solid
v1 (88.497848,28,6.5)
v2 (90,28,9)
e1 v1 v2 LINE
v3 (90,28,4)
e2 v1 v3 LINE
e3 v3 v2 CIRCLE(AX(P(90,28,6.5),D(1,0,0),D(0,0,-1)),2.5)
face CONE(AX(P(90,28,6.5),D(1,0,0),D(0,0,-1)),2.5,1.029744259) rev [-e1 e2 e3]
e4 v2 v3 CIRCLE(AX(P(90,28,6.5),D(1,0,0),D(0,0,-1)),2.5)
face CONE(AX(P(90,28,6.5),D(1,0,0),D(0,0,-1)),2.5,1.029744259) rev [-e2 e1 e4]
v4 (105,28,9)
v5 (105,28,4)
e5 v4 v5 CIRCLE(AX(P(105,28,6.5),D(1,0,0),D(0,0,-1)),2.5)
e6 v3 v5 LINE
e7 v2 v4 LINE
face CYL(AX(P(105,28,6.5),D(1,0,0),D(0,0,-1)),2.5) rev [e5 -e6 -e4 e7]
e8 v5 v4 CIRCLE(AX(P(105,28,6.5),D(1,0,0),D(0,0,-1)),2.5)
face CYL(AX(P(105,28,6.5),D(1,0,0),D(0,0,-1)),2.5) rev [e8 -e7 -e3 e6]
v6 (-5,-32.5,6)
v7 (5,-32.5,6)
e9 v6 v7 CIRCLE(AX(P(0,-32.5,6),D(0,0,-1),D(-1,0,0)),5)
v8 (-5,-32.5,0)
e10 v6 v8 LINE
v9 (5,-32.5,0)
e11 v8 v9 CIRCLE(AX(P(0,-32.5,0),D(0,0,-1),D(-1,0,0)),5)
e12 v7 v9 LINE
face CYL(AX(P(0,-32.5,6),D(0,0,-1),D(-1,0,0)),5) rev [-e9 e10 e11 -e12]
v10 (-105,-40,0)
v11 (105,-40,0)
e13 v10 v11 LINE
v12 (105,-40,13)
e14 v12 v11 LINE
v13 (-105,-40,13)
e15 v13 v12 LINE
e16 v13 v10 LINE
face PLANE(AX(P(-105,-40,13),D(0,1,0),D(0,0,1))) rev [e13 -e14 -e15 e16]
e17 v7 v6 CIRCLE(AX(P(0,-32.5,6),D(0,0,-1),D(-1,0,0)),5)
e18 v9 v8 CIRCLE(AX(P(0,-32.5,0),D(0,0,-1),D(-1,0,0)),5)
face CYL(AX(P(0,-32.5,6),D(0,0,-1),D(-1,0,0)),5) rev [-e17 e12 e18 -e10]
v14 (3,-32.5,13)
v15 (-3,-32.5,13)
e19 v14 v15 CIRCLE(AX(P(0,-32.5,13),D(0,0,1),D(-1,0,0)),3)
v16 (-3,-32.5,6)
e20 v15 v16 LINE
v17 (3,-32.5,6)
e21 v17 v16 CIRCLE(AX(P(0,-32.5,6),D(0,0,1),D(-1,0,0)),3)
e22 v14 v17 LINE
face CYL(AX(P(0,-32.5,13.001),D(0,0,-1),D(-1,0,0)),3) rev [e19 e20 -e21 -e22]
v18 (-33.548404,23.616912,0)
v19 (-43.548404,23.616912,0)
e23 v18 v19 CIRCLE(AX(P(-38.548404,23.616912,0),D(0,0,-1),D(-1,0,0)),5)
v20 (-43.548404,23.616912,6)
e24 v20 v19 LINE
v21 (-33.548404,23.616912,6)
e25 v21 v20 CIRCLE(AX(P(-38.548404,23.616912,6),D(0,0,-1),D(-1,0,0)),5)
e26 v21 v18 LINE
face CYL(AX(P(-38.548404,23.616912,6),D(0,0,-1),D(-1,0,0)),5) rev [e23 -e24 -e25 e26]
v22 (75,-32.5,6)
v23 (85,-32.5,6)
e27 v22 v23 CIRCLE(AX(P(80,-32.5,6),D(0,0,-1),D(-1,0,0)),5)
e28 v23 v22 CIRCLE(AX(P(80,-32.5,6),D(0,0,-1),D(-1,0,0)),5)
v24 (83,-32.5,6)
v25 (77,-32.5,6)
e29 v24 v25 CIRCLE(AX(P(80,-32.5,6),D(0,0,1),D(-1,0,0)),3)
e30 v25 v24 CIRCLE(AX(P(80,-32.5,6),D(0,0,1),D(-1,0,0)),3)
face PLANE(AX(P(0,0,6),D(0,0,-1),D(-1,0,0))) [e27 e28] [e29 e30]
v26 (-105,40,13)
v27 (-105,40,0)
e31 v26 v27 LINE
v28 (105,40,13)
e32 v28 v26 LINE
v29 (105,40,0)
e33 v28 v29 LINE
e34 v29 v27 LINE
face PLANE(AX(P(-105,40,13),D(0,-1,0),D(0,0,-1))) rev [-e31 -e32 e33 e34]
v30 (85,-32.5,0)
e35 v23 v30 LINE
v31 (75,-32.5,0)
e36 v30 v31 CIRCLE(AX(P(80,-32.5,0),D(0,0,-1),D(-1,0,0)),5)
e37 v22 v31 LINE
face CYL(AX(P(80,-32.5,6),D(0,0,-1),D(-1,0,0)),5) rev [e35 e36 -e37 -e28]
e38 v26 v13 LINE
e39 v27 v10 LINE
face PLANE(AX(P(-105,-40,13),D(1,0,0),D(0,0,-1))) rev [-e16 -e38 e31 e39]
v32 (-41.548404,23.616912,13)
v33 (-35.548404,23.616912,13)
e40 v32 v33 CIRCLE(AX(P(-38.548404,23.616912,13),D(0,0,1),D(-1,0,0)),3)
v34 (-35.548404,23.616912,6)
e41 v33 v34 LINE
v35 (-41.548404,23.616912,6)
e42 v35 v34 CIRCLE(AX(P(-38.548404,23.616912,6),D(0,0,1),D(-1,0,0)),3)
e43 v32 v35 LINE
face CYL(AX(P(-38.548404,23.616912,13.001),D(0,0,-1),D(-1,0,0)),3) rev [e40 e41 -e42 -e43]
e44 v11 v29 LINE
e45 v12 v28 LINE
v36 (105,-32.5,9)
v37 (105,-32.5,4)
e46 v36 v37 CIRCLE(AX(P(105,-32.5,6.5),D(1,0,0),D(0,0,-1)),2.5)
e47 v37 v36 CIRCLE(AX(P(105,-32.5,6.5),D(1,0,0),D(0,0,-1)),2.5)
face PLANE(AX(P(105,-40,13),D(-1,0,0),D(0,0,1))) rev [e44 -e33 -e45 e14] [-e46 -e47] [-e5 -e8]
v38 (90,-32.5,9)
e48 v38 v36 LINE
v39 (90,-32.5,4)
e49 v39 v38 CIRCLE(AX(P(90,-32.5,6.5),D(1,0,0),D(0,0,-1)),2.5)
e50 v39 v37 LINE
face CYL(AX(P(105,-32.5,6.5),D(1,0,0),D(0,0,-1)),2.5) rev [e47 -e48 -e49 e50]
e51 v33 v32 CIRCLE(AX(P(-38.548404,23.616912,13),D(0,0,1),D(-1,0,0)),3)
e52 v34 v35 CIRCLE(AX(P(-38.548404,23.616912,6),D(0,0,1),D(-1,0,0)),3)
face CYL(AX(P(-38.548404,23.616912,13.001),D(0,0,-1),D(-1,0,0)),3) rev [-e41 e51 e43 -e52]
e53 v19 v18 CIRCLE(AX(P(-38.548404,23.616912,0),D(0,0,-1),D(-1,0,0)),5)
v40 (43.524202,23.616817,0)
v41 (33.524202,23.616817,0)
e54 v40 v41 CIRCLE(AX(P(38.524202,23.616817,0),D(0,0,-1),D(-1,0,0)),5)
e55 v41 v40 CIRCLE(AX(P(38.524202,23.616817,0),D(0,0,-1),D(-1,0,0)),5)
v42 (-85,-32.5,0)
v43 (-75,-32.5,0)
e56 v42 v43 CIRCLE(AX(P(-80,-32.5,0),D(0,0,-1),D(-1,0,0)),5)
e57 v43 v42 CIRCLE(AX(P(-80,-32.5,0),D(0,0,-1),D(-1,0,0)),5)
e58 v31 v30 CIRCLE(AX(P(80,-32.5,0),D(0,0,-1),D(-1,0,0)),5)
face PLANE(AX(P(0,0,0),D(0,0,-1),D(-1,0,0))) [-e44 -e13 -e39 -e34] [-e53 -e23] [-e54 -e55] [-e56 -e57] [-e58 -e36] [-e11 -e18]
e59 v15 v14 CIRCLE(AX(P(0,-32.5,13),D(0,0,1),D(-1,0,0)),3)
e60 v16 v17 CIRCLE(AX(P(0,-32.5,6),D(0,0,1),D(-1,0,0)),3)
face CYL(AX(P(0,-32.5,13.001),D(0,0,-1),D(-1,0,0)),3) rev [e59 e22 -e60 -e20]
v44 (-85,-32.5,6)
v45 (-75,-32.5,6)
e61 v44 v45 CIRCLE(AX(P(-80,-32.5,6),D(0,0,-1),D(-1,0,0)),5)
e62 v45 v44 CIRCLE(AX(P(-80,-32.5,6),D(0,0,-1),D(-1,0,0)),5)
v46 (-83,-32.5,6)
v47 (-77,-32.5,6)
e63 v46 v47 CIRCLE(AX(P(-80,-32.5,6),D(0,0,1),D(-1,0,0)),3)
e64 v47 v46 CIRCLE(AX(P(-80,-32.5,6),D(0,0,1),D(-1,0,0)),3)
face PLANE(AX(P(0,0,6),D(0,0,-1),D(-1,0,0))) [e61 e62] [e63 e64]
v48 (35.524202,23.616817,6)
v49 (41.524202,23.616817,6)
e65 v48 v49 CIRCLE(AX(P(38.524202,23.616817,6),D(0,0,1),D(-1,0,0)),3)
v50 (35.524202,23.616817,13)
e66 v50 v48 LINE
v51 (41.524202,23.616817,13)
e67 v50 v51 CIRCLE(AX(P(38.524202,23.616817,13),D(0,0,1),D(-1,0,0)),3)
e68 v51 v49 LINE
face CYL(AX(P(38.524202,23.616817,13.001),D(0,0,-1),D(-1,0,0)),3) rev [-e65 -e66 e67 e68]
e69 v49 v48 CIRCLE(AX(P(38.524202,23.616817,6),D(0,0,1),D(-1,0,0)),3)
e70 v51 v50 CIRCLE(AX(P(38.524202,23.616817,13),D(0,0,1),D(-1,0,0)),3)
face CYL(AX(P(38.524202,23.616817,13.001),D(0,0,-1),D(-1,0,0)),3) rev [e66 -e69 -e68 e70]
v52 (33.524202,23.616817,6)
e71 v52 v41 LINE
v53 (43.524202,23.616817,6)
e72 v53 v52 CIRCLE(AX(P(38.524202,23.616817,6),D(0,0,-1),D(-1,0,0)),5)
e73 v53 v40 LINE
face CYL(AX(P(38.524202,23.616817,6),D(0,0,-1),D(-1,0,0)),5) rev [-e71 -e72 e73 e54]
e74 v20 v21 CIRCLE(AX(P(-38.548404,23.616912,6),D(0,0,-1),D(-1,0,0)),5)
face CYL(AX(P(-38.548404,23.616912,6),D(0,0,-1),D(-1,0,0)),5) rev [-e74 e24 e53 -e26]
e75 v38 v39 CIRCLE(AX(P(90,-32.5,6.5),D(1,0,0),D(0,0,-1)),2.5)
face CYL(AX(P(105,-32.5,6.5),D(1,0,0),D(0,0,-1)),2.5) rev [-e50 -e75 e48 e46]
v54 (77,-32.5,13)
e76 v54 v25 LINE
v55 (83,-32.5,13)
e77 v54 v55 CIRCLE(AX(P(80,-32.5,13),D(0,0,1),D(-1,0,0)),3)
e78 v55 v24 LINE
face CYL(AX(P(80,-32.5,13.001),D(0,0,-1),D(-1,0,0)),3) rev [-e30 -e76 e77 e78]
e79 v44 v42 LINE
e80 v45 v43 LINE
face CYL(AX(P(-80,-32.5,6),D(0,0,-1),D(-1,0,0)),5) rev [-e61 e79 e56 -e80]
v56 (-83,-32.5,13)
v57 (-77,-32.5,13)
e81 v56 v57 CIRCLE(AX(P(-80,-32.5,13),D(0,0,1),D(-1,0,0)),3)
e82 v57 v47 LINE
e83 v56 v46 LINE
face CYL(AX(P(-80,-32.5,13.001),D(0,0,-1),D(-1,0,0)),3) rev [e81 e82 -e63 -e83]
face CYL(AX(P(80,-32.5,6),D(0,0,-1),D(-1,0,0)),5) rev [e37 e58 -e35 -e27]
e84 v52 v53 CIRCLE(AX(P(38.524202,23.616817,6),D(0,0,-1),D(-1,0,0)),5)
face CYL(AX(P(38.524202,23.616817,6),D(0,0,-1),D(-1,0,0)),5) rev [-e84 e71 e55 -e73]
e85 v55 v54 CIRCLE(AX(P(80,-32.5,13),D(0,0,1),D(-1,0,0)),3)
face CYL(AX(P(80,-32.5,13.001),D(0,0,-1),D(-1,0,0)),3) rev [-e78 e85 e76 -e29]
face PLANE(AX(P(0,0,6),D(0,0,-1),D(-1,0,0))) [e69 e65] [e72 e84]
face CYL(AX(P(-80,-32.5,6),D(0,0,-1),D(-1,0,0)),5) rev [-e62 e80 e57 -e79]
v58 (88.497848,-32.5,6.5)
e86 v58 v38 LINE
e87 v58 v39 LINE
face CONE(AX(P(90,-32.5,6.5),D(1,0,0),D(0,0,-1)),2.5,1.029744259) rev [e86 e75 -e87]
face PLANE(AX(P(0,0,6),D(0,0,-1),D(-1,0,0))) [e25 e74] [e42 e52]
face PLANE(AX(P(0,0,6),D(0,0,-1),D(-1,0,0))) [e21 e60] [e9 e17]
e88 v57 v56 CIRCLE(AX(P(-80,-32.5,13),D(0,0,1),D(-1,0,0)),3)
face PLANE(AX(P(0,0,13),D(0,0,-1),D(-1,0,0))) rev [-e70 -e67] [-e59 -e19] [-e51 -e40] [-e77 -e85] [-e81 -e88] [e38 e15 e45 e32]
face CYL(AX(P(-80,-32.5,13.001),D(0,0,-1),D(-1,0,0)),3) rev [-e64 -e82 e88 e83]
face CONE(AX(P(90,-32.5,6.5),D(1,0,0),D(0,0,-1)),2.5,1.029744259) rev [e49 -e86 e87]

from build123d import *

# Parameters (mm, degrees)
SKETCH1_W                 = 210
SKETCH1_H                 = 80
BOSS_EXTRUDE1_DEPTH       = 13
SKETCH2_R                 = 5
SKETCH2_R_2               = 3
CUT_EXTRUDE1_DEPTH        = 6
CUT_EXTRUDE2_REACH        = 115.111
SKETCH2_5_R               = 3
M6X1_0_TAPPED_HOLE1_D     = 5
M6X1_0_TAPPED_HOLE1_DEPTH = 15
M6X1_0_TAPPED_HOLE1_TIP   = 1.502151548
SKETCH8_R                 = 5
SKETCH8_R_2               = 3
CUT_EXTRUDE3_DEPTH        = 6
CUT_EXTRUDE4_REACH        = 115.111
SKETCH8_4_R               = 3
M6X1_0_TAPPED_HOLE2_D     = 5
M6X1_0_TAPPED_HOLE2_DEPTH = 15
M6X1_0_TAPPED_HOLE2_TIP   = 1.502151548


with BuildPart() as part:
    # Sketch1 → Boss-Extrude1 (new body)
    with BuildSketch(Plane.XY):
        Rectangle(SKETCH1_W, SKETCH1_H)
    extrude(amount=BOSS_EXTRUDE1_DEPTH)

    # Sketch2 → Cut-Extrude1 (cut)
    # profile 1 of 2: a face of its own
    with BuildSketch(Plane(origin=(0, 0, 0), x_dir=(-1, 0, 0), z_dir=(0, 0, -1))):
        with Locations((-38.524202037, 23.616817232)):
            Circle(SKETCH2_R)
        with Locations((-38.524202037, 23.616817232)):
            Circle(SKETCH2_R_2, mode=Mode.SUBTRACT)
    # profile 2 of 2: a face of its own
    with BuildSketch(Plane(origin=(0, 0, 0), x_dir=(-1, 0, 0), z_dir=(0, 0, -1))):
        with Locations((38.548404074, 23.616912244)):
            Circle(SKETCH2_R)
        with Locations((38.548404074, 23.616912244)):
            Circle(SKETCH2_R_2, mode=Mode.SUBTRACT)
    extrude(amount=-CUT_EXTRUDE1_DEPTH, mode=Mode.SUBTRACT)

    # Sketch2<5> → Cut-Extrude2 (cut, up to next)
    with BuildSketch(Plane(origin=(0, 0, 0), x_dir=(-1, 0, 0), z_dir=(0, 0, -1)), mode=Mode.PRIVATE) as cut_extrude2_sk1:
        with Locations((-38.524202037, 23.616817232)):
            Circle(SKETCH2_5_R)
    cut_extrude2_tool1 = extrude(cut_extrude2_sk1.sketch, amount=-CUT_EXTRUDE2_REACH, mode=Mode.PRIVATE) & part.part
    # Sketch2<5> → Cut-Extrude2 (cut, up to next)
    with BuildSketch(Plane(origin=(0, 0, 0), x_dir=(-1, 0, 0), z_dir=(0, 0, -1)), mode=Mode.PRIVATE) as cut_extrude2_sk2:
        with Locations((38.548404074, 23.616912244)):
            Circle(SKETCH2_5_R)
    cut_extrude2_tool2 = extrude(cut_extrude2_sk2.sketch, amount=-CUT_EXTRUDE2_REACH, mode=Mode.PRIVATE) & part.part
    add(cut_extrude2_tool1.solids().sort_by_distance((38.524202, 23.616817, 0))[0], mode=Mode.SUBTRACT)
    add(cut_extrude2_tool2.solids().sort_by_distance((-38.548404, 23.616912, 0))[0], mode=Mode.SUBTRACT)

    # M6x1.0 Tapped Hole1
    with Locations(Plane(origin=(105, -32.5, 6.5), x_dir=(0, 0, 1), z_dir=(1, 0, 0))):
        with Locations((0, 0)):
            Hole(M6X1_0_TAPPED_HOLE1_D / 2, depth=M6X1_0_TAPPED_HOLE1_DEPTH)
            with Locations((0, 0, -(M6X1_0_TAPPED_HOLE1_DEPTH + M6X1_0_TAPPED_HOLE1_TIP / 2))):  # 118° drill point
                Cone(0, M6X1_0_TAPPED_HOLE1_D / 2, M6X1_0_TAPPED_HOLE1_TIP, mode=Mode.SUBTRACT)

    # Sketch8 → Cut-Extrude3 (cut)
    # profile 1 of 3: a face of its own
    with BuildSketch(Plane(origin=(0, 0, 0), x_dir=(-1, 0, 0), z_dir=(0, 0, -1))):
        with Locations((-80, -32.5)):
            Circle(SKETCH8_R)
        with Locations((-80, -32.5)):
            Circle(SKETCH8_R_2, mode=Mode.SUBTRACT)
    # profile 2 of 3: a face of its own
    with BuildSketch(Plane(origin=(0, 0, 0), x_dir=(-1, 0, 0), z_dir=(0, 0, -1))):
        with Locations((80, -32.5)):
            Circle(SKETCH8_R)
        with Locations((80, -32.5)):
            Circle(SKETCH8_R_2, mode=Mode.SUBTRACT)
    # profile 3 of 3: a face of its own
    with BuildSketch(Plane(origin=(0, 0, 0), x_dir=(-1, 0, 0), z_dir=(0, 0, -1))):
        with Locations((0, -32.5)):
            Circle(SKETCH8_R)
        with Locations((0, -32.5)):
            Circle(SKETCH8_R_2, mode=Mode.SUBTRACT)
    extrude(amount=-CUT_EXTRUDE3_DEPTH, mode=Mode.SUBTRACT)

    # Sketch8<4> → Cut-Extrude4 (cut, up to next)
    with BuildSketch(Plane(origin=(0, 0, 0), x_dir=(-1, 0, 0), z_dir=(0, 0, -1)), mode=Mode.PRIVATE) as cut_extrude4_sk1:
        with Locations((-80, -32.5)):
            Circle(SKETCH8_4_R)
    cut_extrude4_tool1 = extrude(cut_extrude4_sk1.sketch, amount=-CUT_EXTRUDE4_REACH, mode=Mode.PRIVATE) & part.part
    # Sketch8<4> → Cut-Extrude4 (cut, up to next)
    with BuildSketch(Plane(origin=(0, 0, 0), x_dir=(-1, 0, 0), z_dir=(0, 0, -1)), mode=Mode.PRIVATE) as cut_extrude4_sk2:
        with Locations((0, -32.5)):
            Circle(SKETCH8_4_R)
    cut_extrude4_tool2 = extrude(cut_extrude4_sk2.sketch, amount=-CUT_EXTRUDE4_REACH, mode=Mode.PRIVATE) & part.part
    # Sketch8<4> → Cut-Extrude4 (cut, up to next)
    with BuildSketch(Plane(origin=(0, 0, 0), x_dir=(-1, 0, 0), z_dir=(0, 0, -1)), mode=Mode.PRIVATE) as cut_extrude4_sk3:
        with Locations((80, -32.5)):
            Circle(SKETCH8_4_R)
    cut_extrude4_tool3 = extrude(cut_extrude4_sk3.sketch, amount=-CUT_EXTRUDE4_REACH, mode=Mode.PRIVATE) & part.part
    add(cut_extrude4_tool1.solids().sort_by_distance((80, -32.5, 0))[0], mode=Mode.SUBTRACT)
    add(cut_extrude4_tool2.solids().sort_by_distance((0, -32.5, 0))[0], mode=Mode.SUBTRACT)
    add(cut_extrude4_tool3.solids().sort_by_distance((-80, -32.5, 0))[0], mode=Mode.SUBTRACT)

    # M6x1.0 Tapped Hole2
    with Locations(Plane(origin=(105, 28, 6.5), x_dir=(0, 0, 1), z_dir=(1, 0, 0))):
        with Locations((0, 0)):
            Hole(M6X1_0_TAPPED_HOLE2_D / 2, depth=M6X1_0_TAPPED_HOLE2_DEPTH)
            with Locations((0, 0, -(M6X1_0_TAPPED_HOLE2_DEPTH + M6X1_0_TAPPED_HOLE2_TIP / 2))):  # 118° drill point
                Cone(0, M6X1_0_TAPPED_HOLE2_D / 2, M6X1_0_TAPPED_HOLE2_TIP, mode=Mode.SUBTRACT)


solid = part.part
